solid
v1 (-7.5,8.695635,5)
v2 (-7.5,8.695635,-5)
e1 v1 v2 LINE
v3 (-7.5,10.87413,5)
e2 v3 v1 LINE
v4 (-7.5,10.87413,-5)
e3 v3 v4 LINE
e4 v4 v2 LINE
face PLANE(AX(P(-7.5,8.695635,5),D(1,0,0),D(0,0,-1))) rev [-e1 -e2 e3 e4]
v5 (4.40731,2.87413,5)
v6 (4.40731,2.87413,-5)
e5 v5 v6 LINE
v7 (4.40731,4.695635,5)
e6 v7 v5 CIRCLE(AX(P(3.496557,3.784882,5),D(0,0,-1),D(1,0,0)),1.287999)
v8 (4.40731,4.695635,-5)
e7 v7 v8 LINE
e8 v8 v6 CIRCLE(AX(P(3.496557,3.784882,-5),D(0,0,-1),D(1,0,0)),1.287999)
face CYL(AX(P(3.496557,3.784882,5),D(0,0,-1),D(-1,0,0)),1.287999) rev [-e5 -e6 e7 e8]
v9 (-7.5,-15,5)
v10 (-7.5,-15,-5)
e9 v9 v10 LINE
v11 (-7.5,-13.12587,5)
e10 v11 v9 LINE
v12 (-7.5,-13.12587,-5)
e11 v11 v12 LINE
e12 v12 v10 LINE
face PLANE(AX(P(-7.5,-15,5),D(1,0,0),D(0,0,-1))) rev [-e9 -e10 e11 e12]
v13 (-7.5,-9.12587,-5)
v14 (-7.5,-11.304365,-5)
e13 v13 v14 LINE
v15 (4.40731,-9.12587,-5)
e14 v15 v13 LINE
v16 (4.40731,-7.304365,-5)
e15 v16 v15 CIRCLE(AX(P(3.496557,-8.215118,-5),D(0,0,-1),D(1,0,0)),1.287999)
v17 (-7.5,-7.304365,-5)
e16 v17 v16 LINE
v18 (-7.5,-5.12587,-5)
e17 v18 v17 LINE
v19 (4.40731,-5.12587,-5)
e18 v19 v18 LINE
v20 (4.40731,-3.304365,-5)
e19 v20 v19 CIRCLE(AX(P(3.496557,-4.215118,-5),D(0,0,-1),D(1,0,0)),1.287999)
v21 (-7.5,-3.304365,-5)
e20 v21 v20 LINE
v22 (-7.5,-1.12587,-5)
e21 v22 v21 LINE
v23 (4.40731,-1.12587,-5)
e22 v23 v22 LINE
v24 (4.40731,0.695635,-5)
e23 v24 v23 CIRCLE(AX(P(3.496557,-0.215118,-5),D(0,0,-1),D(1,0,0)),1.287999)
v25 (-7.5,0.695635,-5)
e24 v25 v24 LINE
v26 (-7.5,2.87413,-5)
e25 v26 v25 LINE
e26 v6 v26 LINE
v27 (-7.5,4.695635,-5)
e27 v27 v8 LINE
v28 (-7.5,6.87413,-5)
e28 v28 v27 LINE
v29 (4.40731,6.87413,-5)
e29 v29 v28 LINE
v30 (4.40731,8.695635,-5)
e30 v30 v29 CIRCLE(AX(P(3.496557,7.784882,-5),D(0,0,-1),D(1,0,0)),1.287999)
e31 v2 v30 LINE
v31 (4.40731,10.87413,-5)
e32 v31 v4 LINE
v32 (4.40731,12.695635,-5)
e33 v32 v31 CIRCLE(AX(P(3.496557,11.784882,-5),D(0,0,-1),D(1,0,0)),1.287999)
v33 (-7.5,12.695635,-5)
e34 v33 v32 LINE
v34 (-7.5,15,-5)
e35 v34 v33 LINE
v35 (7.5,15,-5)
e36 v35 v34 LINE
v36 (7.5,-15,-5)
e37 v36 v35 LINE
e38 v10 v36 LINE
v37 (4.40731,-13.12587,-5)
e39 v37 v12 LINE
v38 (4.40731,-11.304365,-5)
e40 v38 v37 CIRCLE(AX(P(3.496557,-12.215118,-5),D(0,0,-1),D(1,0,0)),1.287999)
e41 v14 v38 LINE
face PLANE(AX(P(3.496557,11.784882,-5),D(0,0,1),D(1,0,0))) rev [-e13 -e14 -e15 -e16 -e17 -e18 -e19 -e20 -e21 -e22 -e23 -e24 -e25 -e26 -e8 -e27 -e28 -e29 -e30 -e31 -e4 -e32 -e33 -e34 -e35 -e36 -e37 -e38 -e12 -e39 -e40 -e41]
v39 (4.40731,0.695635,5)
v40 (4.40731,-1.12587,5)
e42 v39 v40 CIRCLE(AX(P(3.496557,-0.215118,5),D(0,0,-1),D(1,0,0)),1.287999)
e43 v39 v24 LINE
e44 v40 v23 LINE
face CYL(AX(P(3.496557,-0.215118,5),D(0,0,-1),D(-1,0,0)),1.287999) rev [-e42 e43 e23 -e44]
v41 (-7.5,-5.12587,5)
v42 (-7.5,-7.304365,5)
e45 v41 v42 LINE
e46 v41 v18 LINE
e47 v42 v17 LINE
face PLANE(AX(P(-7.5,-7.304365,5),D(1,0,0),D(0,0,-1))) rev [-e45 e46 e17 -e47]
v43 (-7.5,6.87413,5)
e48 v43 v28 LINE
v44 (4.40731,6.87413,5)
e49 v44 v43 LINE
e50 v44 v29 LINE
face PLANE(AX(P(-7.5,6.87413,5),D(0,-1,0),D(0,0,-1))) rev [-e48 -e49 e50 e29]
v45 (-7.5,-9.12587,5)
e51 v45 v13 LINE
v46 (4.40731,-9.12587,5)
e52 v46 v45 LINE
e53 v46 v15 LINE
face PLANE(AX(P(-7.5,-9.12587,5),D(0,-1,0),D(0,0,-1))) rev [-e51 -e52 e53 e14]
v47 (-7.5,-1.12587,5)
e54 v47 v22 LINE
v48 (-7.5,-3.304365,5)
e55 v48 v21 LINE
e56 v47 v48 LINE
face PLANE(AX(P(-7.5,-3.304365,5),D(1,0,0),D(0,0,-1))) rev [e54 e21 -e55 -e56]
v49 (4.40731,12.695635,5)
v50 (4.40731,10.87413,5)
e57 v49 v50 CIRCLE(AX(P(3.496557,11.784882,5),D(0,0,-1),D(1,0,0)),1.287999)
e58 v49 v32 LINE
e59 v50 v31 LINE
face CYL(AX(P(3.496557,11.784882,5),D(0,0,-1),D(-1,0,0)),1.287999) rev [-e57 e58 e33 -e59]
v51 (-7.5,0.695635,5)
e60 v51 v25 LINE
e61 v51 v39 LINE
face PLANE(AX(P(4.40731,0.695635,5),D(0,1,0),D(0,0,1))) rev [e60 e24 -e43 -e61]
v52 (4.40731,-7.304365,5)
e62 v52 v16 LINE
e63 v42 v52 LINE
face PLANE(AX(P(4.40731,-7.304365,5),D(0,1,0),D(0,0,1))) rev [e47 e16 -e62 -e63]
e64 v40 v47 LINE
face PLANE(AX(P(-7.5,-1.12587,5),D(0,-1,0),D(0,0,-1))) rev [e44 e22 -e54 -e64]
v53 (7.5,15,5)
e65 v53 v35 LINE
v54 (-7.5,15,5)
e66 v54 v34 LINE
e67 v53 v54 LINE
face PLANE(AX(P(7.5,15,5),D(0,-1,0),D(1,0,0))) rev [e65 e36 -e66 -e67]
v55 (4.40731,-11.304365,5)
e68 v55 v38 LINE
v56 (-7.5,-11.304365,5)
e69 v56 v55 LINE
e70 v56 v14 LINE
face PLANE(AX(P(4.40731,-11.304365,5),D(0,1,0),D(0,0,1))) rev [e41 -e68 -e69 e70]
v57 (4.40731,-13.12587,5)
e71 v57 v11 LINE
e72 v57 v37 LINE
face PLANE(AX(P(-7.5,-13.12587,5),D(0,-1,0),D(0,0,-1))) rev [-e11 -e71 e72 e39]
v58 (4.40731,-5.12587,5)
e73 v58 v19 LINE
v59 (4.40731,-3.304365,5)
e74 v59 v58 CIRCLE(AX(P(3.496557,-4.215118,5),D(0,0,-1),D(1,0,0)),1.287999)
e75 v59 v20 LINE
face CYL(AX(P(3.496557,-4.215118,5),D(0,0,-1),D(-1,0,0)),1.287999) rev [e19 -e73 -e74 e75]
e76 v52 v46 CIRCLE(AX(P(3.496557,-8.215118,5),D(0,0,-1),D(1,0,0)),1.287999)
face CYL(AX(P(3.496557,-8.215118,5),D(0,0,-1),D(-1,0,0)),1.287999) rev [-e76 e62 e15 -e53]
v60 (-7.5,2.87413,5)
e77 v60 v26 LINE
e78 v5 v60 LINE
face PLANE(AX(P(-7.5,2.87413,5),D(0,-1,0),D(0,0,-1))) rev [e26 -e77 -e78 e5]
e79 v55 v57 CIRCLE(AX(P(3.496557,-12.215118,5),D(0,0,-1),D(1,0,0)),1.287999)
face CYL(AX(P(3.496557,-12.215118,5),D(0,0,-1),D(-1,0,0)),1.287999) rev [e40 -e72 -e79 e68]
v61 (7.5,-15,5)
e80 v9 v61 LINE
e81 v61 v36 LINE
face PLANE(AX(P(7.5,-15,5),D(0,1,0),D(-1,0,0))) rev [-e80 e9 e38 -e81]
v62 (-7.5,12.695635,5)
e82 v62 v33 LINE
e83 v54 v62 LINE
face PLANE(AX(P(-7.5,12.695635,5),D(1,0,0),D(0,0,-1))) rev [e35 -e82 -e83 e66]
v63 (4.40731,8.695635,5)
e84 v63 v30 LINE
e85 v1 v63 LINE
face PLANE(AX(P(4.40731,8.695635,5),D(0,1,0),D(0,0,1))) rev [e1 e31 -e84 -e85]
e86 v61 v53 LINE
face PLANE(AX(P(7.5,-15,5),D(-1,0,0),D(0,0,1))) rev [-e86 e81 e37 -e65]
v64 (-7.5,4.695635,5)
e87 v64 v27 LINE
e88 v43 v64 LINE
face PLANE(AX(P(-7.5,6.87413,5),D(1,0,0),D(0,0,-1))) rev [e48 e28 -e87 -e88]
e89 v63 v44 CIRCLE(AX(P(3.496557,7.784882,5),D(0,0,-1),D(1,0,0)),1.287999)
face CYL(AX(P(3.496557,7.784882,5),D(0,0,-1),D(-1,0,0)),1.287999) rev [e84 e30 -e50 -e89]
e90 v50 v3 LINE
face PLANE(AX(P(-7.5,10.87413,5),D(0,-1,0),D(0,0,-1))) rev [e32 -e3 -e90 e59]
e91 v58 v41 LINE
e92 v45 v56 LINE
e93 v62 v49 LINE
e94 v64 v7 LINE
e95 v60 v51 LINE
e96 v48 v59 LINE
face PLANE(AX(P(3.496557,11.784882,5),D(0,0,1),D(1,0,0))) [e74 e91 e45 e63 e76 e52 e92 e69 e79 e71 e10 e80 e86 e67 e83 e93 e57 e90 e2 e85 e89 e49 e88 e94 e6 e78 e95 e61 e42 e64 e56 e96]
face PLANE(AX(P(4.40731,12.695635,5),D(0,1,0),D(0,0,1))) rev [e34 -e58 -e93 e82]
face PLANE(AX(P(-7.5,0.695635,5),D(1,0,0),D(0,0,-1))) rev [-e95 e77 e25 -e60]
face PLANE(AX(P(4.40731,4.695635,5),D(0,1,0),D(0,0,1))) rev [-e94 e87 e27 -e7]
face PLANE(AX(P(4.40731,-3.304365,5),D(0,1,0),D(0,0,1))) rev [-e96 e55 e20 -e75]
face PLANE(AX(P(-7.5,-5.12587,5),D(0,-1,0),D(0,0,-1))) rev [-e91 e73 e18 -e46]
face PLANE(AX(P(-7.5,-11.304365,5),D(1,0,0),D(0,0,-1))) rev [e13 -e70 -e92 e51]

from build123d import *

# Parameters (mm, degrees)
EXTRUDE_1_DEPTH = 5


with BuildPart() as part:
    # 草图1 → 凸台-拉伸1 (new, symmetric)
    with BuildSketch(Plane.XY):
        with BuildLine():
            Line((7.5, -15), (-7.5, -15))
            Line((-7.5, -15), (-7.5, -13.125870379))
            Line((-7.5, -13.125870379), (4.407309833, -13.125870379))
            ThreePointArc((4.407309833, -13.125870379), (4.784555906, -12.215117792), (4.407309833, -11.304365204))
            Line((4.407309833, -11.304365204), (-7.5, -11.304365204))
            Line((-7.5, -11.304365204), (-7.5, -9.125870379))
            Line((-7.5, -9.125870379), (4.407309833, -9.125870379))
            ThreePointArc((4.407309833, -9.125870379), (4.784555906, -8.215117792), (4.407309833, -7.304365204))
            Line((4.407309833, -7.304365204), (-7.5, -7.304365204))
            Line((-7.5, -7.304365204), (-7.5, -5.125870379))
            Line((-7.5, -5.125870379), (4.407309833, -5.125870379))
            ThreePointArc((4.407309833, -5.125870379), (4.784555906, -4.215117792), (4.407309833, -3.304365204))
            Line((4.407309833, -3.304365204), (-7.5, -3.304365204))
            Line((-7.5, -3.304365204), (-7.5, -1.125870379))
            Line((-7.5, -1.125870379), (4.407309833, -1.125870379))
            ThreePointArc((4.407309833, -1.125870379), (4.784555906, -0.215117792), (4.407309833, 0.695634796))
            Line((4.407309833, 0.695634796), (-7.5, 0.695634796))
            Line((-7.5, 0.695634796), (-7.5, 2.874129621))
            Line((-7.5, 2.874129621), (4.407309833, 2.874129621))
            ThreePointArc((4.407309833, 2.874129621), (4.784555906, 3.784882208), (4.407309833, 4.695634796))
            Line((4.407309833, 4.695634796), (-7.5, 4.695634796))
            Line((-7.5, 4.695634796), (-7.5, 6.874129621))
            Line((-7.5, 6.874129621), (4.407309833, 6.874129621))
            ThreePointArc((4.407309833, 6.874129621), (4.784555906, 7.784882208), (4.407309833, 8.695634796))
            Line((4.407309833, 8.695634796), (-7.5, 8.695634796))
            Line((-7.5, 8.695634796), (-7.5, 10.874129621))
            Line((-7.5, 10.874129621), (4.407309833, 10.874129621))
            ThreePointArc((4.407309833, 10.874129621), (4.784555906, 11.784882208), (4.407309833, 12.695634796))
            Line((4.407309833, 12.695634796), (-7.5, 12.695634796))
            Line((-7.5, 12.695634796), (-7.5, 15))
            Line((-7.5, 15), (7.5, 15))
            Line((7.5, 15), (7.5, -15))
        make_face()
    extrude(amount=EXTRUDE_1_DEPTH, both=True)


solid = part.part
